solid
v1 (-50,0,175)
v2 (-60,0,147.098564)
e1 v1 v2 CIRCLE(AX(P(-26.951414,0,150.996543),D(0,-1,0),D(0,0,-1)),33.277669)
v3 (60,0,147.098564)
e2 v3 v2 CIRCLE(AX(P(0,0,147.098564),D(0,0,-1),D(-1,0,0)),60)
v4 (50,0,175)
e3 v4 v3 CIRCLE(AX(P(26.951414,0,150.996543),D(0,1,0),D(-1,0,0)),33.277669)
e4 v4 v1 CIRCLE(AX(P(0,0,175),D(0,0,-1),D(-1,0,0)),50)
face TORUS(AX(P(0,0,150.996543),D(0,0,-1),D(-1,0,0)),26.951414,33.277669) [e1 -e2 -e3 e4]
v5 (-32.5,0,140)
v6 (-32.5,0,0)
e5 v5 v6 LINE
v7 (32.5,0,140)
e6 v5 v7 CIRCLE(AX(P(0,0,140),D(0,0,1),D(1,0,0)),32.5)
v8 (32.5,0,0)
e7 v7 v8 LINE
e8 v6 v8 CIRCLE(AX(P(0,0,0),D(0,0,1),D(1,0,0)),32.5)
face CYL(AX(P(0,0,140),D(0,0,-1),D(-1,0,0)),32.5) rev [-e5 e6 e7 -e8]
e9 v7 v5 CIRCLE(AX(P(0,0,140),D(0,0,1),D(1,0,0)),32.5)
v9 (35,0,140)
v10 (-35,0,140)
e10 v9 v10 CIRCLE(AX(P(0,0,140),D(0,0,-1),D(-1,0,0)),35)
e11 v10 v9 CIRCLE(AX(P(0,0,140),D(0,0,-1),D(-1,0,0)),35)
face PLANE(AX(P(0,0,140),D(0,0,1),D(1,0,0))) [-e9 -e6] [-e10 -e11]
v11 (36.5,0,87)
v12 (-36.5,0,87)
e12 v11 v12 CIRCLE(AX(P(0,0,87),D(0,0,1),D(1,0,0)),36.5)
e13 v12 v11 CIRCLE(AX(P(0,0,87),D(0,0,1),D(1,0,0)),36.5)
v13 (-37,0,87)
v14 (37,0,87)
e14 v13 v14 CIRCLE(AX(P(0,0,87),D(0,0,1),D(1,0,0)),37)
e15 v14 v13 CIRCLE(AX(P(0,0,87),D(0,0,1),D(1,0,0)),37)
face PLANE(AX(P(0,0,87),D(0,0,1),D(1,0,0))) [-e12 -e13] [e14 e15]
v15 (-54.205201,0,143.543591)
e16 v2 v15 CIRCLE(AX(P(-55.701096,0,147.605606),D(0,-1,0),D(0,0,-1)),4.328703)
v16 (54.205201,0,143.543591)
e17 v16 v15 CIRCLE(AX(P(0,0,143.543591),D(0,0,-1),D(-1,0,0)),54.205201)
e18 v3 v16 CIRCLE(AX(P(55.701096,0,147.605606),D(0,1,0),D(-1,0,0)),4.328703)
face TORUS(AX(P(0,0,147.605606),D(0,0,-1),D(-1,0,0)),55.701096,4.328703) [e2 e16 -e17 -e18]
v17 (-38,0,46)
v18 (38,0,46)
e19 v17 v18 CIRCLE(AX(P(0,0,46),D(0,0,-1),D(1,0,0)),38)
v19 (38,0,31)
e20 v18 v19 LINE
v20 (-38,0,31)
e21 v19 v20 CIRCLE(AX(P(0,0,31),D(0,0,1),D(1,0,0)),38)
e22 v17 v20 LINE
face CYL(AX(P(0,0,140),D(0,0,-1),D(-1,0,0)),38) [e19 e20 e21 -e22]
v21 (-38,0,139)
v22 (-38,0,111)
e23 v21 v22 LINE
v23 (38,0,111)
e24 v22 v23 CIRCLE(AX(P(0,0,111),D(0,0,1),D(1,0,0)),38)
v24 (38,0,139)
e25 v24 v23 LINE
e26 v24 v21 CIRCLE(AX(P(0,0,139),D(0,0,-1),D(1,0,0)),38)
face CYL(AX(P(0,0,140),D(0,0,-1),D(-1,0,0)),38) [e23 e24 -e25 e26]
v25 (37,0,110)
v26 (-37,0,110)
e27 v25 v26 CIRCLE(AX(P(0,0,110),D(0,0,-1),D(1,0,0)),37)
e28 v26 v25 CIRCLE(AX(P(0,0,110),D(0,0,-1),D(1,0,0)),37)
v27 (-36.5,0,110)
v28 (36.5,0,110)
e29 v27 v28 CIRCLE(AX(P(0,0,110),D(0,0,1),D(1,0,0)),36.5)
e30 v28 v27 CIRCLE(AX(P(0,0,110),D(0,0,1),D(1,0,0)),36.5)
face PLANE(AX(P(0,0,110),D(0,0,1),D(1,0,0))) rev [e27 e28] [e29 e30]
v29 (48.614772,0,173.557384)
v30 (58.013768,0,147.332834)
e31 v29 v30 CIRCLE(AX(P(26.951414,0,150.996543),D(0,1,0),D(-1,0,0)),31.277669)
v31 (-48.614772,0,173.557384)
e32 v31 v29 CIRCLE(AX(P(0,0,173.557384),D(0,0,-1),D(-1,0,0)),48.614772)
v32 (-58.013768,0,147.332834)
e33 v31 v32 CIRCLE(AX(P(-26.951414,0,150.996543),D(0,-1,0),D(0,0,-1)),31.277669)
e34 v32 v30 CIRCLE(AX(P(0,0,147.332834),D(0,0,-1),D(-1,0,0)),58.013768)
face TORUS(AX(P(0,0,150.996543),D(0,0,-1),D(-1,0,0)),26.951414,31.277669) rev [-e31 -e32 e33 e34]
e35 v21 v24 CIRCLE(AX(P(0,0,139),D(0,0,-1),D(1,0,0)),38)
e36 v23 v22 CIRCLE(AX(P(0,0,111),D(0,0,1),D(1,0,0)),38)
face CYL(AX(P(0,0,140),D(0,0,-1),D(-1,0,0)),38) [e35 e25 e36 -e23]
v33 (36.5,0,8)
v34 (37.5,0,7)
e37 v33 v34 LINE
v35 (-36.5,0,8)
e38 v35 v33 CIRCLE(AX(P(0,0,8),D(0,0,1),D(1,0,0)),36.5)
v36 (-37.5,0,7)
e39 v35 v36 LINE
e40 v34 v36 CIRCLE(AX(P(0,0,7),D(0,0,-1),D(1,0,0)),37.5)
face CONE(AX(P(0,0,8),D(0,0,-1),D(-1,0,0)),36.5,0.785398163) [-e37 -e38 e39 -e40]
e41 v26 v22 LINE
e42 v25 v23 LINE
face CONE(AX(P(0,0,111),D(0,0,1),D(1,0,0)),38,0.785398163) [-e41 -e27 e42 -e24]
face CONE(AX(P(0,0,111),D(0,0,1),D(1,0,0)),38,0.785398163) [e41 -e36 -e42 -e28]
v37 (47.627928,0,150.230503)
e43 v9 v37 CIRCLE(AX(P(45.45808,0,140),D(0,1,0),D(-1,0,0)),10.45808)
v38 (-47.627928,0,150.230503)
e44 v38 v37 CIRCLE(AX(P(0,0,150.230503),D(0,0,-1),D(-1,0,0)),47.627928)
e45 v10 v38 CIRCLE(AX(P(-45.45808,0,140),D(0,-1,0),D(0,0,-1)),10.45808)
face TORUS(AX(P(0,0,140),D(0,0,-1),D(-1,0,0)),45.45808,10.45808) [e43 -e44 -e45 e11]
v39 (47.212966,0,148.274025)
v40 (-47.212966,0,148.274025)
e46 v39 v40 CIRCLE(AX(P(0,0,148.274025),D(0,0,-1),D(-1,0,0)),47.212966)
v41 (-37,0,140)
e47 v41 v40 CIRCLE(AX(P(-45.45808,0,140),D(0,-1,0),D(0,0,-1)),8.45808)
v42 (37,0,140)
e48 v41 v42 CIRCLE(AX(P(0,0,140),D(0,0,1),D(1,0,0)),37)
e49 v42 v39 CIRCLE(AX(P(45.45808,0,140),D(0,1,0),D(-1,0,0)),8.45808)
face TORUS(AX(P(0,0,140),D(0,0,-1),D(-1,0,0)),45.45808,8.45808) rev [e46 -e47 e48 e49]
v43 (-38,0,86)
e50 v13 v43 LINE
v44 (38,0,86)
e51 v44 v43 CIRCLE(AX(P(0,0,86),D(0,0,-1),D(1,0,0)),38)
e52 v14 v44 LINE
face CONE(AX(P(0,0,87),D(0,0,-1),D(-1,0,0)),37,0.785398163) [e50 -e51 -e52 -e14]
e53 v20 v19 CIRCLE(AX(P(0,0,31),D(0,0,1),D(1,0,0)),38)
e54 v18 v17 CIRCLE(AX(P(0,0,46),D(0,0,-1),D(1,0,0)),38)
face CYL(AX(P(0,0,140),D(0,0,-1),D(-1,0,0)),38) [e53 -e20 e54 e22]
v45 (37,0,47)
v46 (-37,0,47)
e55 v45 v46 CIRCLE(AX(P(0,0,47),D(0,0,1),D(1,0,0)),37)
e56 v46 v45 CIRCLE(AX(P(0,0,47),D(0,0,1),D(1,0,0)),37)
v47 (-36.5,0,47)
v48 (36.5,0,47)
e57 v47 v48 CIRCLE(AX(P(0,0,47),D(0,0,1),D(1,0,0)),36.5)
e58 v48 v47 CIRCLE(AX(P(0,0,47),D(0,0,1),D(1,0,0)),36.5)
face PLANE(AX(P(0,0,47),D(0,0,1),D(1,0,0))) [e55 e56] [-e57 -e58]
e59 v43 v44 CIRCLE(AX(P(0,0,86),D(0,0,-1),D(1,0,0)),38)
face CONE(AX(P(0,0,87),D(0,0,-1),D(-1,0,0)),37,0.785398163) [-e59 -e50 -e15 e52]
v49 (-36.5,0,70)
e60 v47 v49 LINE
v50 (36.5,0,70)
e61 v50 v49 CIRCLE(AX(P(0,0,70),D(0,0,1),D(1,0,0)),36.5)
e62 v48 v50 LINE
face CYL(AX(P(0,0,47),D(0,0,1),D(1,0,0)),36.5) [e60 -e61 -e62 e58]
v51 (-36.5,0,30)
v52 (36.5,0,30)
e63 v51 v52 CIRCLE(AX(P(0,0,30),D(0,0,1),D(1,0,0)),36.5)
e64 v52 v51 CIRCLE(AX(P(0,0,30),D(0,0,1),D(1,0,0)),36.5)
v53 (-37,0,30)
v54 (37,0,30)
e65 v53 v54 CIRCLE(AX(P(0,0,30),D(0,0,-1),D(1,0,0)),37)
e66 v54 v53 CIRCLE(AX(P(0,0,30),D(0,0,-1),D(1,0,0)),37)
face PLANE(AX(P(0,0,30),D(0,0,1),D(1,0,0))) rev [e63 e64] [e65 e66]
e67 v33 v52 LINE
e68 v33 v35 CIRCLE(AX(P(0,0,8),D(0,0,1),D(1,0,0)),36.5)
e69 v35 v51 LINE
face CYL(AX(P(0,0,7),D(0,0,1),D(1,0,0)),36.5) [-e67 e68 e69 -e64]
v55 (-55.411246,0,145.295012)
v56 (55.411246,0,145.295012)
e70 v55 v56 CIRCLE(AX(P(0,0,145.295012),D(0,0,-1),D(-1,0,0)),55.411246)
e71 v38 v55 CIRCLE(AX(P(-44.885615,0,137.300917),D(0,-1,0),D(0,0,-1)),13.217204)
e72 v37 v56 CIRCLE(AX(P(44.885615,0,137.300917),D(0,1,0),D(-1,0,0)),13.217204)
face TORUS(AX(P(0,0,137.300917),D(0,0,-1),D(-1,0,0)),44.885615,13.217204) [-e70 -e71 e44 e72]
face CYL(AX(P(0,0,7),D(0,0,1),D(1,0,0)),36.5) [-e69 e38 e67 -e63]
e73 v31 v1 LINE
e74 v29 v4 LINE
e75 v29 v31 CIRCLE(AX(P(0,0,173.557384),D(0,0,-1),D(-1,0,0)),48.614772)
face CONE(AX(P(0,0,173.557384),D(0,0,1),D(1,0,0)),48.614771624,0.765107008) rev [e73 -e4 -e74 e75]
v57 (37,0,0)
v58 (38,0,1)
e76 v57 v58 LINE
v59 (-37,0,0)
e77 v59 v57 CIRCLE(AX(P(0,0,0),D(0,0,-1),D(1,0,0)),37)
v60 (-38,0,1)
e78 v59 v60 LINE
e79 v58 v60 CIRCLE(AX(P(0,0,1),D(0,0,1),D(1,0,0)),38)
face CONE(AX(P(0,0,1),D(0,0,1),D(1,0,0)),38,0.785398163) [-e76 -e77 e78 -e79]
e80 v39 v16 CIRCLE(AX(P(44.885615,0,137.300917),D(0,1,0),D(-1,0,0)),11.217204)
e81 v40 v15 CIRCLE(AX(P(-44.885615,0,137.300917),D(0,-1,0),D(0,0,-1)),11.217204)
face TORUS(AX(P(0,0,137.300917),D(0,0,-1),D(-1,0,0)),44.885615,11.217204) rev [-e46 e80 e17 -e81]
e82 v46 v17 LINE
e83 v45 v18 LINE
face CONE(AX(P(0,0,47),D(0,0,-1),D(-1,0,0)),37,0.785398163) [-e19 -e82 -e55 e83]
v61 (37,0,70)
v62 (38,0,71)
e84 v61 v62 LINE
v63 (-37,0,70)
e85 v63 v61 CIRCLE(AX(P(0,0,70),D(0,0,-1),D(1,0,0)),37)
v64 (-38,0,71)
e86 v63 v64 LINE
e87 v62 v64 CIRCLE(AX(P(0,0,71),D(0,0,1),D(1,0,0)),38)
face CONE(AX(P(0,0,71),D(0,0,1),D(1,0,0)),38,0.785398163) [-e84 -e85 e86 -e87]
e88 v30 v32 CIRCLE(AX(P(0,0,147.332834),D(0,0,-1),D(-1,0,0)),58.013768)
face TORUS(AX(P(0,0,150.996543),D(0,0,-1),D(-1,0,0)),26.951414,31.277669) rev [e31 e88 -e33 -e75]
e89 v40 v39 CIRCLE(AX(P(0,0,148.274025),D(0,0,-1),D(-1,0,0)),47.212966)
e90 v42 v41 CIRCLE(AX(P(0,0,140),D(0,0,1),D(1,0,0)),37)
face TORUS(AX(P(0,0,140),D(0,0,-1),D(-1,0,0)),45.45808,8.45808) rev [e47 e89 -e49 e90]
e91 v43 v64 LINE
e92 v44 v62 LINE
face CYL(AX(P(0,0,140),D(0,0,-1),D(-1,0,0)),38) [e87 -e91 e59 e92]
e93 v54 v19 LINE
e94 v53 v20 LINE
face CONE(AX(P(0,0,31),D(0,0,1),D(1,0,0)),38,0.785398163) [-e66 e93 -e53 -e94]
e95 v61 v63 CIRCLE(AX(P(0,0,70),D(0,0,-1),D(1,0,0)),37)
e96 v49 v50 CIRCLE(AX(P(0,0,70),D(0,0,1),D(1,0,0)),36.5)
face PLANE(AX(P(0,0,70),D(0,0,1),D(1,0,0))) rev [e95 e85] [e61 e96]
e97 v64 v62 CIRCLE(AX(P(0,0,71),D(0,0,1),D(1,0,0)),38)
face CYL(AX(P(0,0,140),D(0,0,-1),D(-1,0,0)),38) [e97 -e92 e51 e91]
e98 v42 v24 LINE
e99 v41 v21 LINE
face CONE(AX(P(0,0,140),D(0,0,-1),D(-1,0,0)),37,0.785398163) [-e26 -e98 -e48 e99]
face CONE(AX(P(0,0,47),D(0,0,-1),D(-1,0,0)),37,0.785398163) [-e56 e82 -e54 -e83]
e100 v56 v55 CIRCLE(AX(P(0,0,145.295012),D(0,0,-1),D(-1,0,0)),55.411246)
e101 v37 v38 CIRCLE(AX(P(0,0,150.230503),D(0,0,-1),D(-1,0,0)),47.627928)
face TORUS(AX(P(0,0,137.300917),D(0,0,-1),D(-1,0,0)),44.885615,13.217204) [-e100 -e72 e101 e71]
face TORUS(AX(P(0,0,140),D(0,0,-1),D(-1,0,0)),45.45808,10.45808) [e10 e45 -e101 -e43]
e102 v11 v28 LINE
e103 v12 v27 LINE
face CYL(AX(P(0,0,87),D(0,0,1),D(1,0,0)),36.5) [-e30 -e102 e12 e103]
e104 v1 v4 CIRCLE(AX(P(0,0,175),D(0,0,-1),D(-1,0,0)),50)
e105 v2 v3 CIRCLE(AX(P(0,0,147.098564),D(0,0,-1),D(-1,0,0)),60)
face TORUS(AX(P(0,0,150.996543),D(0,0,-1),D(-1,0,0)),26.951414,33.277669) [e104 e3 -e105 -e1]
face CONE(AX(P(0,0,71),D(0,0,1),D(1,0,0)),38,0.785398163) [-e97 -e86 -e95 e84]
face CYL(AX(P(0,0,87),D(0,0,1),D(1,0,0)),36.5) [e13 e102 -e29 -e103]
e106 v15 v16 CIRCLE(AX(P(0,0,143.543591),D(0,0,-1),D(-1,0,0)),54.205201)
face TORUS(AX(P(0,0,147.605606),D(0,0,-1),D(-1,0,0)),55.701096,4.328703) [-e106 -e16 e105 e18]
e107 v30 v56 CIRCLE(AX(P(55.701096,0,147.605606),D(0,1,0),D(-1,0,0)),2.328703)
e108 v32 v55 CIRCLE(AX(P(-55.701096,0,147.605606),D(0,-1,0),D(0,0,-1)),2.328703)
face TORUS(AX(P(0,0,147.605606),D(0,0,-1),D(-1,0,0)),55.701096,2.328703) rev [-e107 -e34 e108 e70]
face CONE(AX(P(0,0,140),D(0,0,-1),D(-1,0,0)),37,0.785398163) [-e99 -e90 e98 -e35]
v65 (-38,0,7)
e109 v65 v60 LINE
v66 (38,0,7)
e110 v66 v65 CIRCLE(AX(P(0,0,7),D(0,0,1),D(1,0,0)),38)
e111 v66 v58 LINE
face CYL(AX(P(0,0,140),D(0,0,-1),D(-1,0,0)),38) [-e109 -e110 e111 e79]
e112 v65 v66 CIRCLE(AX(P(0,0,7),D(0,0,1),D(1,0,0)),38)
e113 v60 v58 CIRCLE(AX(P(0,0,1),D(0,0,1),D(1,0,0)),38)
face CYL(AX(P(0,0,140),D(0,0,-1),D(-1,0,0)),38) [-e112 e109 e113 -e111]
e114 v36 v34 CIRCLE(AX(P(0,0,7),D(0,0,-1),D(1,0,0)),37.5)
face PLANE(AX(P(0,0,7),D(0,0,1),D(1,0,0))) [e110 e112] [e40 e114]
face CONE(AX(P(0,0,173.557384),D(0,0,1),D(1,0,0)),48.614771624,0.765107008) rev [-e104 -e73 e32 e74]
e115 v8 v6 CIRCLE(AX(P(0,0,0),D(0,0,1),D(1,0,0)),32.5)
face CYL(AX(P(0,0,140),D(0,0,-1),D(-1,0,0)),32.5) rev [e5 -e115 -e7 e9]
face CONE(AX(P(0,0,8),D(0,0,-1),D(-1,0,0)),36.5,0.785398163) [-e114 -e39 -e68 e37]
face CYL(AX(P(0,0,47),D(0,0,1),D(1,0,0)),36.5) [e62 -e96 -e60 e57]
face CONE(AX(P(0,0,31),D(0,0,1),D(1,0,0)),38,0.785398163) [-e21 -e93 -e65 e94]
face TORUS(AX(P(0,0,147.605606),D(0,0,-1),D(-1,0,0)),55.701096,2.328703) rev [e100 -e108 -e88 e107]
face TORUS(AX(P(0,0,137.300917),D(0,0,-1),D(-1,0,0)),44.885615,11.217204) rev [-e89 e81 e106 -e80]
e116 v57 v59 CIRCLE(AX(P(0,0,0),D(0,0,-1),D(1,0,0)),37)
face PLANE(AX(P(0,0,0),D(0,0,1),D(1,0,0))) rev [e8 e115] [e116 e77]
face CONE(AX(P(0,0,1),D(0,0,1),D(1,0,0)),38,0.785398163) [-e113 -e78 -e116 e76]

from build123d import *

# Parameters (mm, degrees)
SKETCH_1_R             = 38
SKETCH_1_R_2           = 32.5
EXTRUDE_1_DEPTH        = 140
CHAMFER_1_SIZE         = 1
CUT_EXTRUDE_START      = -23
SKETCH_2_R             = 38
SKETCH_2_R_2           = 36.5
CUT_EXTRUDE_1_DEPTH    = 23
PATTERN_LINEAR_1_COUNT = 3
PATTERN_LINEAR_1_PITCH = 40
CHAMFER_2_SIZE         = 1


with BuildPart() as part:
    # 草图1 → 凸台-拉伸1 (new body)
    with BuildSketch(Plane.XY):
        Circle(SKETCH_1_R)
        Circle(SKETCH_1_R_2, mode=Mode.SUBTRACT)
    extrude(amount=EXTRUDE_1_DEPTH)

    # 倒角1
    chamfer_1_edges = [part.edges().sort_by_distance(p)[0] for p in [
        (-38, 0, 140),
    ]]
    chamfer(chamfer_1_edges, length=CHAMFER_1_SIZE)

    # 草图2 → 切除-拉伸1 (cut)
    with BuildSketch(Plane.XY.offset(110).offset(CUT_EXTRUDE_START)):
        Circle(SKETCH_2_R)
        Circle(SKETCH_2_R_2, mode=Mode.SUBTRACT)
    cut_extrude_1 = extrude(amount=CUT_EXTRUDE_1_DEPTH, mode=Mode.SUBTRACT)

    # 阵列(线性)1: 切除-拉伸1 ×3
    with Locations(*[(0, 0, -i * PATTERN_LINEAR_1_PITCH) for i in range(1, PATTERN_LINEAR_1_COUNT)]):
        add(cut_extrude_1, mode=Mode.SUBTRACT)

    # 倒角2
    chamfer_2_edges = [part.edges().sort_by_distance(p)[0] for p in [
        (-38, 0, 87),
        (-38, 0, 110),
        (-38, 0, 0),
        (-38, 0, 47),
        (-38, 0, 70),
        (-36.5, 0, 7),
        (-38, 0, 30),
    ]]
    chamfer(chamfer_2_edges, length=CHAMFER_2_SIZE)

    # 草图3 → 旋转1 (revolve)
    with BuildSketch(Plane(origin=(0, 0, 0), x_dir=(1, 0, 0), z_dir=(0, 1, 0)), mode=Mode.PRIVATE) as revolve_1_sk:
        with BuildLine():
            Line((50, -175), (48.614771624, -173.557383507))
            ThreePointArc((48.614771624, -173.557383507), (56.395121663, -161.54929973), (58.013767993, -147.332833686))
            ThreePointArc((58.013767993, -147.332833686), (57.136760156, -145.772105393), (55.411246429, -145.295012185))
            ThreePointArc((55.411246429, -145.295012185), (51.963704542, -148.463135482), (47.627927509, -150.230502962))
            ThreePointArc((47.627927509, -150.230502962), (38.874805833, -148.126003692), (35, -140))
            Line((35, -140), (37, -140))
            ThreePointArc((37, -140), (40.133789135, -146.571989199), (47.212966464, -148.274024664))
            ThreePointArc((47.212966464, -148.274024664), (51.171077472, -146.59169845), (54.205200918, -143.543590978))
            ThreePointArc((54.205200918, -143.543590978), (57.964649, -143.915891309), (60, -147.098563727))
            ThreePointArc((60, -147.098563727), (58.277851947, -162.224078714), (50, -175))
        make_face()
    revolve(revolve_1_sk.sketch.rotate(Axis((0, 0, 140), (0, 0, 1)), 180), axis=Axis((0, 0, 140), (0, 0, 1)))


solid = part.part
